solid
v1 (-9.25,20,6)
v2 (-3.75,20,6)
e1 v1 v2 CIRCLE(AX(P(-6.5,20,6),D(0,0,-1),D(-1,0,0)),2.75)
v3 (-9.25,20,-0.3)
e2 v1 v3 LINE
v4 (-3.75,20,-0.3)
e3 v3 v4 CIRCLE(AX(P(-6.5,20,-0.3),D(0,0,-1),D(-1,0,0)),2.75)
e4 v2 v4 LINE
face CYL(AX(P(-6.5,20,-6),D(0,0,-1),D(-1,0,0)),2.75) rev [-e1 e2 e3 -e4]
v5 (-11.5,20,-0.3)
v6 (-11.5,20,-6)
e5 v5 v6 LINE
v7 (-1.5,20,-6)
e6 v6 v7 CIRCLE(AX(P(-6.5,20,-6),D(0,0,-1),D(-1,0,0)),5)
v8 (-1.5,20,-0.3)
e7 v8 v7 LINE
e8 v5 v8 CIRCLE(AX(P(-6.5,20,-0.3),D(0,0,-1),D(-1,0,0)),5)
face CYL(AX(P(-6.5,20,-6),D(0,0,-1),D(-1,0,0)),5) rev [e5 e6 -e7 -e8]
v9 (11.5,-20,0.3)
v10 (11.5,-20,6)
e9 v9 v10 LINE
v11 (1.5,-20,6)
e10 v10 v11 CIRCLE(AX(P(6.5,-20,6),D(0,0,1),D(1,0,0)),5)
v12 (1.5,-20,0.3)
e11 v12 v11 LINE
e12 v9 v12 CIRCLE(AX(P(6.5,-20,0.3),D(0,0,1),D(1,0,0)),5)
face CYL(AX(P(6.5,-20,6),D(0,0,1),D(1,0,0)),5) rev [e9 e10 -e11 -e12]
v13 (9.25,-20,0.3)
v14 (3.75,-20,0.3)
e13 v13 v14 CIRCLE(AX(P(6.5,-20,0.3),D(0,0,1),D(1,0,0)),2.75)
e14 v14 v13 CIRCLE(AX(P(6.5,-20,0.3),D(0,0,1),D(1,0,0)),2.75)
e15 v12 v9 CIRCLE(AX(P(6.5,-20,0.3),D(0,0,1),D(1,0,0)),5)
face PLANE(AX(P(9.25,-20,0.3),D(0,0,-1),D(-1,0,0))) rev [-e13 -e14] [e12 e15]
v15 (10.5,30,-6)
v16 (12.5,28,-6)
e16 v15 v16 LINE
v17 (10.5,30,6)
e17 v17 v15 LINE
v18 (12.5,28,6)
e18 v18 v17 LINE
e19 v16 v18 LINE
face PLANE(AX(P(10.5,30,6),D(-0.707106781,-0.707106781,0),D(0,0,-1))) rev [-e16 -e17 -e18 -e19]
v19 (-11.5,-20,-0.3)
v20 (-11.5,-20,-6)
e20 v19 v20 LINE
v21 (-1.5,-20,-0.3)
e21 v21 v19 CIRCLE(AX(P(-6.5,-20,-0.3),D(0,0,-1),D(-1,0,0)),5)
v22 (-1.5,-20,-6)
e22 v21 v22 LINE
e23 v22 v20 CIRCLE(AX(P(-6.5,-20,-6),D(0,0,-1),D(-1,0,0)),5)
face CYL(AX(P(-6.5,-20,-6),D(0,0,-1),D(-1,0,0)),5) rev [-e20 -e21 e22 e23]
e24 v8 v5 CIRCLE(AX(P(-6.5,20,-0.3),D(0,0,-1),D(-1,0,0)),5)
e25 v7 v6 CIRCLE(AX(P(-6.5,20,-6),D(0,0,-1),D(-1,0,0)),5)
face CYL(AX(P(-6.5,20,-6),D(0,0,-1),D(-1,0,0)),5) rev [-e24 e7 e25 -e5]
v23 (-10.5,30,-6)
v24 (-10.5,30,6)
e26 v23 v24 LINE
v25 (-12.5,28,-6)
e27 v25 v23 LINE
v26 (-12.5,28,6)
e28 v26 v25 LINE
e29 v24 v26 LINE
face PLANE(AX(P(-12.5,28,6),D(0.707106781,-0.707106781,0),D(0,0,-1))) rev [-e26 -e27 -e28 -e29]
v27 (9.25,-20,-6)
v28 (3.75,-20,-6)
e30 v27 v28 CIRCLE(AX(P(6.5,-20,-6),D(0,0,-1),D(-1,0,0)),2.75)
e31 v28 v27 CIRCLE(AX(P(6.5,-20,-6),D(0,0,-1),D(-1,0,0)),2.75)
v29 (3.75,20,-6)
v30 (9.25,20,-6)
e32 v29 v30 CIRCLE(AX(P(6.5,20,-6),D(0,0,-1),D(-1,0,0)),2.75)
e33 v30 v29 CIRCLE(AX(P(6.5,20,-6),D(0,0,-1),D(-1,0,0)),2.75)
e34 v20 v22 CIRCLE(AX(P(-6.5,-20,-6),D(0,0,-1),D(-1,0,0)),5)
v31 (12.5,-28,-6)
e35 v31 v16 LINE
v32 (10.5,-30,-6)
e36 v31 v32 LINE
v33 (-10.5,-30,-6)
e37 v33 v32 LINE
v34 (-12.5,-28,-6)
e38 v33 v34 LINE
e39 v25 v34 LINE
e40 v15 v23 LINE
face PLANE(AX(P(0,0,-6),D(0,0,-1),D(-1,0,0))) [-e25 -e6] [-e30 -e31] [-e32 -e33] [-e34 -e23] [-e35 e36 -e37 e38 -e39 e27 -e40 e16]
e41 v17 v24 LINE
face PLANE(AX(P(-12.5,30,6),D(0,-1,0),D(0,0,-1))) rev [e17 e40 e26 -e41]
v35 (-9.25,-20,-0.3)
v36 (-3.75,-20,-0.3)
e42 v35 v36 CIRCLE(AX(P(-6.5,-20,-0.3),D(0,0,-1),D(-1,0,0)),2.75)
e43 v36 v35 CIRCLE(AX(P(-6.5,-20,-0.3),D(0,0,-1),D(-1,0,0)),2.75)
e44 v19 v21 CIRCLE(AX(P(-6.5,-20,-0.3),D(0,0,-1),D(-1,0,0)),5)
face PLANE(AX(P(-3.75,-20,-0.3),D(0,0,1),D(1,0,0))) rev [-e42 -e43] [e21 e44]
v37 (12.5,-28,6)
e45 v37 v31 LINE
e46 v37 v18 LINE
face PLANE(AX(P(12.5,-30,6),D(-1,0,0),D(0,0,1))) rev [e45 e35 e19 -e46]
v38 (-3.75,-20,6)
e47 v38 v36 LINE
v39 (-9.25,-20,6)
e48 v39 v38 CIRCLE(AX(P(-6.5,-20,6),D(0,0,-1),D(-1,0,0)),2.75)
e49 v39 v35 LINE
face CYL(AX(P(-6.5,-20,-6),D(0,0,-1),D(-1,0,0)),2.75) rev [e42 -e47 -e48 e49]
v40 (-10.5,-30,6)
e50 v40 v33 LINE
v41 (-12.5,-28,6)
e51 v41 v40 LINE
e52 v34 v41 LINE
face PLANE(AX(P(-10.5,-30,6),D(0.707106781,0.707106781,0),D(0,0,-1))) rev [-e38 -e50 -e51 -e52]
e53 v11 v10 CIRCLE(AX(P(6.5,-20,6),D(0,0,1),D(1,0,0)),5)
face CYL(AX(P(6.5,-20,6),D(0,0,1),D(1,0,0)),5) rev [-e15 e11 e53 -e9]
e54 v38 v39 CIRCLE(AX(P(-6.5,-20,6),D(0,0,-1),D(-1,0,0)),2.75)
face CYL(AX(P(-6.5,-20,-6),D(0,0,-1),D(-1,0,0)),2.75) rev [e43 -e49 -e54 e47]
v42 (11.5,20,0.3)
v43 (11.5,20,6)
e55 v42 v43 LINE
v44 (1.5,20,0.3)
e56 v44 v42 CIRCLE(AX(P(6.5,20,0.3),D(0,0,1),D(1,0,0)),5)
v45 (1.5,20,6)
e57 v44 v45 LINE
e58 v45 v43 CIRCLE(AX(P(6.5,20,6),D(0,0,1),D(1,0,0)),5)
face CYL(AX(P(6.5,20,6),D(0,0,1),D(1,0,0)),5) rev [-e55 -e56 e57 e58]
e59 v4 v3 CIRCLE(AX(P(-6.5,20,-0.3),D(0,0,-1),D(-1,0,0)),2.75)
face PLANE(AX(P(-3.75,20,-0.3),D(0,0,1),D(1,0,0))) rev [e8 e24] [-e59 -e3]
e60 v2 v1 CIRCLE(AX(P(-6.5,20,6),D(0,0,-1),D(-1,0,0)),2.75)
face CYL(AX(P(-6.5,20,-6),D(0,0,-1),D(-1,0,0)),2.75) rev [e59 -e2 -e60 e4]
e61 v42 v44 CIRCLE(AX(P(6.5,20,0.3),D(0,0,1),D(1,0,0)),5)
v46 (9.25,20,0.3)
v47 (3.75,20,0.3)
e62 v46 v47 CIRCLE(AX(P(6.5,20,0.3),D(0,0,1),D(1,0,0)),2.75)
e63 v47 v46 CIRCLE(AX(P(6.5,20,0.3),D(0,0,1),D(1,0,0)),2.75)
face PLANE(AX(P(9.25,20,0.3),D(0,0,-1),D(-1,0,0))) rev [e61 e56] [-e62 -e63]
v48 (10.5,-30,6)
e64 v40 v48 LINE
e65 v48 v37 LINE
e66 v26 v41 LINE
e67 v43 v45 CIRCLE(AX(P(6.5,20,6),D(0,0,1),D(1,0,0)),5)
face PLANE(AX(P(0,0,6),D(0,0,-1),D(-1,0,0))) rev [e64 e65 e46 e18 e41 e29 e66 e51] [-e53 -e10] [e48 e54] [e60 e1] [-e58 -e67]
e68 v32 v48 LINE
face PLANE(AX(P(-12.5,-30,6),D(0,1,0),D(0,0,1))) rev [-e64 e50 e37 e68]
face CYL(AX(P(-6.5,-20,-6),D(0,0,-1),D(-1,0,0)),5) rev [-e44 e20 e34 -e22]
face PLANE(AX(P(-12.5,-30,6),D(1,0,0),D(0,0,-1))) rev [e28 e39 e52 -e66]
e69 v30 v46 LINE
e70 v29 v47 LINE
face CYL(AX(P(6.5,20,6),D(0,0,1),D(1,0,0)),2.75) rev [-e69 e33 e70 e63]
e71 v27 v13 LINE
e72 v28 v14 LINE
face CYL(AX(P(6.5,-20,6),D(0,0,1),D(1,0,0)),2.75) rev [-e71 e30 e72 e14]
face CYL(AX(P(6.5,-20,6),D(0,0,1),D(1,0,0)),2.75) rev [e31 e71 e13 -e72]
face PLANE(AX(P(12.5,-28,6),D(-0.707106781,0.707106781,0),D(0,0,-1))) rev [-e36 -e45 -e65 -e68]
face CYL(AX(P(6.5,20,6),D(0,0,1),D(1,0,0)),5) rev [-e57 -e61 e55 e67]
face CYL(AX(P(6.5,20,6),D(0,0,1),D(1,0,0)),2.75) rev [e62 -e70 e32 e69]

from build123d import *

# Parameters (mm, degrees)
SKETCH_1_W                   = 25
SKETCH_1_H                   = 60
EXTRUDE_1_DEPTH              = 6
CHAMFER_1_SIZE               = 2
HOLE_WIZARD_M5_1_D           = 5.5
HOLE_WIZARD_M5_1_DEPTH       = 12.4
HOLE_WIZARD_M5_1_CBORE_D     = 10
HOLE_WIZARD_M5_1_CBORE_DEPTH = 5.7
HOLE_WIZARD_M5_1_TIP         = 1.652366702
HOLE_WIZARD_M5_2_D           = 5.5
HOLE_WIZARD_M5_2_DEPTH       = 12.4
HOLE_WIZARD_M5_2_CBORE_D     = 10
HOLE_WIZARD_M5_2_CBORE_DEPTH = 5.7
HOLE_WIZARD_M5_2_TIP         = 1.652366702


with BuildPart() as part:
    # 草图1 → 凸台-拉伸1 (new, symmetric)
    with BuildSketch(Plane.XY):
        Rectangle(SKETCH_1_W, SKETCH_1_H)
    extrude(amount=EXTRUDE_1_DEPTH, both=True)

    # 倒角1
    chamfer_1_edges = [part.edges().sort_by_distance(p)[0] for p in [
        (12.5, -30, 0),
        (-12.5, -30, 0),
        (-12.5, 30, 0),
        (12.5, 30, 0),
    ]]
    chamfer(chamfer_1_edges, length=CHAMFER_1_SIZE)

    # M5 六角圆柱头螺钉的柱形沉头孔1
    with Locations(Plane(origin=(0, 0, -6), x_dir=(-1, 0, 0), z_dir=(0, 0, -1))):
        with Locations((6.5, 20), (6.5, -20)):
            CounterBoreHole(HOLE_WIZARD_M5_1_D / 2, HOLE_WIZARD_M5_1_CBORE_D / 2, HOLE_WIZARD_M5_1_CBORE_DEPTH, depth=HOLE_WIZARD_M5_1_DEPTH)
            with Locations((0, 0, -(HOLE_WIZARD_M5_1_DEPTH + HOLE_WIZARD_M5_1_TIP / 2))):  # 118° drill point
                Cone(0, HOLE_WIZARD_M5_1_D / 2, HOLE_WIZARD_M5_1_TIP, mode=Mode.SUBTRACT)

    # M5 六角圆柱头螺钉的柱形沉头孔2
    with Locations(Plane.XY.offset(6)):
        with Locations((6.5, 20), (6.5, -20)):
            CounterBoreHole(HOLE_WIZARD_M5_2_D / 2, HOLE_WIZARD_M5_2_CBORE_D / 2, HOLE_WIZARD_M5_2_CBORE_DEPTH, depth=HOLE_WIZARD_M5_2_DEPTH)
            with Locations((0, 0, -(HOLE_WIZARD_M5_2_DEPTH + HOLE_WIZARD_M5_2_TIP / 2))):  # 118° drill point
                Cone(0, HOLE_WIZARD_M5_2_D / 2, HOLE_WIZARD_M5_2_TIP, mode=Mode.SUBTRACT)


solid = part.part
